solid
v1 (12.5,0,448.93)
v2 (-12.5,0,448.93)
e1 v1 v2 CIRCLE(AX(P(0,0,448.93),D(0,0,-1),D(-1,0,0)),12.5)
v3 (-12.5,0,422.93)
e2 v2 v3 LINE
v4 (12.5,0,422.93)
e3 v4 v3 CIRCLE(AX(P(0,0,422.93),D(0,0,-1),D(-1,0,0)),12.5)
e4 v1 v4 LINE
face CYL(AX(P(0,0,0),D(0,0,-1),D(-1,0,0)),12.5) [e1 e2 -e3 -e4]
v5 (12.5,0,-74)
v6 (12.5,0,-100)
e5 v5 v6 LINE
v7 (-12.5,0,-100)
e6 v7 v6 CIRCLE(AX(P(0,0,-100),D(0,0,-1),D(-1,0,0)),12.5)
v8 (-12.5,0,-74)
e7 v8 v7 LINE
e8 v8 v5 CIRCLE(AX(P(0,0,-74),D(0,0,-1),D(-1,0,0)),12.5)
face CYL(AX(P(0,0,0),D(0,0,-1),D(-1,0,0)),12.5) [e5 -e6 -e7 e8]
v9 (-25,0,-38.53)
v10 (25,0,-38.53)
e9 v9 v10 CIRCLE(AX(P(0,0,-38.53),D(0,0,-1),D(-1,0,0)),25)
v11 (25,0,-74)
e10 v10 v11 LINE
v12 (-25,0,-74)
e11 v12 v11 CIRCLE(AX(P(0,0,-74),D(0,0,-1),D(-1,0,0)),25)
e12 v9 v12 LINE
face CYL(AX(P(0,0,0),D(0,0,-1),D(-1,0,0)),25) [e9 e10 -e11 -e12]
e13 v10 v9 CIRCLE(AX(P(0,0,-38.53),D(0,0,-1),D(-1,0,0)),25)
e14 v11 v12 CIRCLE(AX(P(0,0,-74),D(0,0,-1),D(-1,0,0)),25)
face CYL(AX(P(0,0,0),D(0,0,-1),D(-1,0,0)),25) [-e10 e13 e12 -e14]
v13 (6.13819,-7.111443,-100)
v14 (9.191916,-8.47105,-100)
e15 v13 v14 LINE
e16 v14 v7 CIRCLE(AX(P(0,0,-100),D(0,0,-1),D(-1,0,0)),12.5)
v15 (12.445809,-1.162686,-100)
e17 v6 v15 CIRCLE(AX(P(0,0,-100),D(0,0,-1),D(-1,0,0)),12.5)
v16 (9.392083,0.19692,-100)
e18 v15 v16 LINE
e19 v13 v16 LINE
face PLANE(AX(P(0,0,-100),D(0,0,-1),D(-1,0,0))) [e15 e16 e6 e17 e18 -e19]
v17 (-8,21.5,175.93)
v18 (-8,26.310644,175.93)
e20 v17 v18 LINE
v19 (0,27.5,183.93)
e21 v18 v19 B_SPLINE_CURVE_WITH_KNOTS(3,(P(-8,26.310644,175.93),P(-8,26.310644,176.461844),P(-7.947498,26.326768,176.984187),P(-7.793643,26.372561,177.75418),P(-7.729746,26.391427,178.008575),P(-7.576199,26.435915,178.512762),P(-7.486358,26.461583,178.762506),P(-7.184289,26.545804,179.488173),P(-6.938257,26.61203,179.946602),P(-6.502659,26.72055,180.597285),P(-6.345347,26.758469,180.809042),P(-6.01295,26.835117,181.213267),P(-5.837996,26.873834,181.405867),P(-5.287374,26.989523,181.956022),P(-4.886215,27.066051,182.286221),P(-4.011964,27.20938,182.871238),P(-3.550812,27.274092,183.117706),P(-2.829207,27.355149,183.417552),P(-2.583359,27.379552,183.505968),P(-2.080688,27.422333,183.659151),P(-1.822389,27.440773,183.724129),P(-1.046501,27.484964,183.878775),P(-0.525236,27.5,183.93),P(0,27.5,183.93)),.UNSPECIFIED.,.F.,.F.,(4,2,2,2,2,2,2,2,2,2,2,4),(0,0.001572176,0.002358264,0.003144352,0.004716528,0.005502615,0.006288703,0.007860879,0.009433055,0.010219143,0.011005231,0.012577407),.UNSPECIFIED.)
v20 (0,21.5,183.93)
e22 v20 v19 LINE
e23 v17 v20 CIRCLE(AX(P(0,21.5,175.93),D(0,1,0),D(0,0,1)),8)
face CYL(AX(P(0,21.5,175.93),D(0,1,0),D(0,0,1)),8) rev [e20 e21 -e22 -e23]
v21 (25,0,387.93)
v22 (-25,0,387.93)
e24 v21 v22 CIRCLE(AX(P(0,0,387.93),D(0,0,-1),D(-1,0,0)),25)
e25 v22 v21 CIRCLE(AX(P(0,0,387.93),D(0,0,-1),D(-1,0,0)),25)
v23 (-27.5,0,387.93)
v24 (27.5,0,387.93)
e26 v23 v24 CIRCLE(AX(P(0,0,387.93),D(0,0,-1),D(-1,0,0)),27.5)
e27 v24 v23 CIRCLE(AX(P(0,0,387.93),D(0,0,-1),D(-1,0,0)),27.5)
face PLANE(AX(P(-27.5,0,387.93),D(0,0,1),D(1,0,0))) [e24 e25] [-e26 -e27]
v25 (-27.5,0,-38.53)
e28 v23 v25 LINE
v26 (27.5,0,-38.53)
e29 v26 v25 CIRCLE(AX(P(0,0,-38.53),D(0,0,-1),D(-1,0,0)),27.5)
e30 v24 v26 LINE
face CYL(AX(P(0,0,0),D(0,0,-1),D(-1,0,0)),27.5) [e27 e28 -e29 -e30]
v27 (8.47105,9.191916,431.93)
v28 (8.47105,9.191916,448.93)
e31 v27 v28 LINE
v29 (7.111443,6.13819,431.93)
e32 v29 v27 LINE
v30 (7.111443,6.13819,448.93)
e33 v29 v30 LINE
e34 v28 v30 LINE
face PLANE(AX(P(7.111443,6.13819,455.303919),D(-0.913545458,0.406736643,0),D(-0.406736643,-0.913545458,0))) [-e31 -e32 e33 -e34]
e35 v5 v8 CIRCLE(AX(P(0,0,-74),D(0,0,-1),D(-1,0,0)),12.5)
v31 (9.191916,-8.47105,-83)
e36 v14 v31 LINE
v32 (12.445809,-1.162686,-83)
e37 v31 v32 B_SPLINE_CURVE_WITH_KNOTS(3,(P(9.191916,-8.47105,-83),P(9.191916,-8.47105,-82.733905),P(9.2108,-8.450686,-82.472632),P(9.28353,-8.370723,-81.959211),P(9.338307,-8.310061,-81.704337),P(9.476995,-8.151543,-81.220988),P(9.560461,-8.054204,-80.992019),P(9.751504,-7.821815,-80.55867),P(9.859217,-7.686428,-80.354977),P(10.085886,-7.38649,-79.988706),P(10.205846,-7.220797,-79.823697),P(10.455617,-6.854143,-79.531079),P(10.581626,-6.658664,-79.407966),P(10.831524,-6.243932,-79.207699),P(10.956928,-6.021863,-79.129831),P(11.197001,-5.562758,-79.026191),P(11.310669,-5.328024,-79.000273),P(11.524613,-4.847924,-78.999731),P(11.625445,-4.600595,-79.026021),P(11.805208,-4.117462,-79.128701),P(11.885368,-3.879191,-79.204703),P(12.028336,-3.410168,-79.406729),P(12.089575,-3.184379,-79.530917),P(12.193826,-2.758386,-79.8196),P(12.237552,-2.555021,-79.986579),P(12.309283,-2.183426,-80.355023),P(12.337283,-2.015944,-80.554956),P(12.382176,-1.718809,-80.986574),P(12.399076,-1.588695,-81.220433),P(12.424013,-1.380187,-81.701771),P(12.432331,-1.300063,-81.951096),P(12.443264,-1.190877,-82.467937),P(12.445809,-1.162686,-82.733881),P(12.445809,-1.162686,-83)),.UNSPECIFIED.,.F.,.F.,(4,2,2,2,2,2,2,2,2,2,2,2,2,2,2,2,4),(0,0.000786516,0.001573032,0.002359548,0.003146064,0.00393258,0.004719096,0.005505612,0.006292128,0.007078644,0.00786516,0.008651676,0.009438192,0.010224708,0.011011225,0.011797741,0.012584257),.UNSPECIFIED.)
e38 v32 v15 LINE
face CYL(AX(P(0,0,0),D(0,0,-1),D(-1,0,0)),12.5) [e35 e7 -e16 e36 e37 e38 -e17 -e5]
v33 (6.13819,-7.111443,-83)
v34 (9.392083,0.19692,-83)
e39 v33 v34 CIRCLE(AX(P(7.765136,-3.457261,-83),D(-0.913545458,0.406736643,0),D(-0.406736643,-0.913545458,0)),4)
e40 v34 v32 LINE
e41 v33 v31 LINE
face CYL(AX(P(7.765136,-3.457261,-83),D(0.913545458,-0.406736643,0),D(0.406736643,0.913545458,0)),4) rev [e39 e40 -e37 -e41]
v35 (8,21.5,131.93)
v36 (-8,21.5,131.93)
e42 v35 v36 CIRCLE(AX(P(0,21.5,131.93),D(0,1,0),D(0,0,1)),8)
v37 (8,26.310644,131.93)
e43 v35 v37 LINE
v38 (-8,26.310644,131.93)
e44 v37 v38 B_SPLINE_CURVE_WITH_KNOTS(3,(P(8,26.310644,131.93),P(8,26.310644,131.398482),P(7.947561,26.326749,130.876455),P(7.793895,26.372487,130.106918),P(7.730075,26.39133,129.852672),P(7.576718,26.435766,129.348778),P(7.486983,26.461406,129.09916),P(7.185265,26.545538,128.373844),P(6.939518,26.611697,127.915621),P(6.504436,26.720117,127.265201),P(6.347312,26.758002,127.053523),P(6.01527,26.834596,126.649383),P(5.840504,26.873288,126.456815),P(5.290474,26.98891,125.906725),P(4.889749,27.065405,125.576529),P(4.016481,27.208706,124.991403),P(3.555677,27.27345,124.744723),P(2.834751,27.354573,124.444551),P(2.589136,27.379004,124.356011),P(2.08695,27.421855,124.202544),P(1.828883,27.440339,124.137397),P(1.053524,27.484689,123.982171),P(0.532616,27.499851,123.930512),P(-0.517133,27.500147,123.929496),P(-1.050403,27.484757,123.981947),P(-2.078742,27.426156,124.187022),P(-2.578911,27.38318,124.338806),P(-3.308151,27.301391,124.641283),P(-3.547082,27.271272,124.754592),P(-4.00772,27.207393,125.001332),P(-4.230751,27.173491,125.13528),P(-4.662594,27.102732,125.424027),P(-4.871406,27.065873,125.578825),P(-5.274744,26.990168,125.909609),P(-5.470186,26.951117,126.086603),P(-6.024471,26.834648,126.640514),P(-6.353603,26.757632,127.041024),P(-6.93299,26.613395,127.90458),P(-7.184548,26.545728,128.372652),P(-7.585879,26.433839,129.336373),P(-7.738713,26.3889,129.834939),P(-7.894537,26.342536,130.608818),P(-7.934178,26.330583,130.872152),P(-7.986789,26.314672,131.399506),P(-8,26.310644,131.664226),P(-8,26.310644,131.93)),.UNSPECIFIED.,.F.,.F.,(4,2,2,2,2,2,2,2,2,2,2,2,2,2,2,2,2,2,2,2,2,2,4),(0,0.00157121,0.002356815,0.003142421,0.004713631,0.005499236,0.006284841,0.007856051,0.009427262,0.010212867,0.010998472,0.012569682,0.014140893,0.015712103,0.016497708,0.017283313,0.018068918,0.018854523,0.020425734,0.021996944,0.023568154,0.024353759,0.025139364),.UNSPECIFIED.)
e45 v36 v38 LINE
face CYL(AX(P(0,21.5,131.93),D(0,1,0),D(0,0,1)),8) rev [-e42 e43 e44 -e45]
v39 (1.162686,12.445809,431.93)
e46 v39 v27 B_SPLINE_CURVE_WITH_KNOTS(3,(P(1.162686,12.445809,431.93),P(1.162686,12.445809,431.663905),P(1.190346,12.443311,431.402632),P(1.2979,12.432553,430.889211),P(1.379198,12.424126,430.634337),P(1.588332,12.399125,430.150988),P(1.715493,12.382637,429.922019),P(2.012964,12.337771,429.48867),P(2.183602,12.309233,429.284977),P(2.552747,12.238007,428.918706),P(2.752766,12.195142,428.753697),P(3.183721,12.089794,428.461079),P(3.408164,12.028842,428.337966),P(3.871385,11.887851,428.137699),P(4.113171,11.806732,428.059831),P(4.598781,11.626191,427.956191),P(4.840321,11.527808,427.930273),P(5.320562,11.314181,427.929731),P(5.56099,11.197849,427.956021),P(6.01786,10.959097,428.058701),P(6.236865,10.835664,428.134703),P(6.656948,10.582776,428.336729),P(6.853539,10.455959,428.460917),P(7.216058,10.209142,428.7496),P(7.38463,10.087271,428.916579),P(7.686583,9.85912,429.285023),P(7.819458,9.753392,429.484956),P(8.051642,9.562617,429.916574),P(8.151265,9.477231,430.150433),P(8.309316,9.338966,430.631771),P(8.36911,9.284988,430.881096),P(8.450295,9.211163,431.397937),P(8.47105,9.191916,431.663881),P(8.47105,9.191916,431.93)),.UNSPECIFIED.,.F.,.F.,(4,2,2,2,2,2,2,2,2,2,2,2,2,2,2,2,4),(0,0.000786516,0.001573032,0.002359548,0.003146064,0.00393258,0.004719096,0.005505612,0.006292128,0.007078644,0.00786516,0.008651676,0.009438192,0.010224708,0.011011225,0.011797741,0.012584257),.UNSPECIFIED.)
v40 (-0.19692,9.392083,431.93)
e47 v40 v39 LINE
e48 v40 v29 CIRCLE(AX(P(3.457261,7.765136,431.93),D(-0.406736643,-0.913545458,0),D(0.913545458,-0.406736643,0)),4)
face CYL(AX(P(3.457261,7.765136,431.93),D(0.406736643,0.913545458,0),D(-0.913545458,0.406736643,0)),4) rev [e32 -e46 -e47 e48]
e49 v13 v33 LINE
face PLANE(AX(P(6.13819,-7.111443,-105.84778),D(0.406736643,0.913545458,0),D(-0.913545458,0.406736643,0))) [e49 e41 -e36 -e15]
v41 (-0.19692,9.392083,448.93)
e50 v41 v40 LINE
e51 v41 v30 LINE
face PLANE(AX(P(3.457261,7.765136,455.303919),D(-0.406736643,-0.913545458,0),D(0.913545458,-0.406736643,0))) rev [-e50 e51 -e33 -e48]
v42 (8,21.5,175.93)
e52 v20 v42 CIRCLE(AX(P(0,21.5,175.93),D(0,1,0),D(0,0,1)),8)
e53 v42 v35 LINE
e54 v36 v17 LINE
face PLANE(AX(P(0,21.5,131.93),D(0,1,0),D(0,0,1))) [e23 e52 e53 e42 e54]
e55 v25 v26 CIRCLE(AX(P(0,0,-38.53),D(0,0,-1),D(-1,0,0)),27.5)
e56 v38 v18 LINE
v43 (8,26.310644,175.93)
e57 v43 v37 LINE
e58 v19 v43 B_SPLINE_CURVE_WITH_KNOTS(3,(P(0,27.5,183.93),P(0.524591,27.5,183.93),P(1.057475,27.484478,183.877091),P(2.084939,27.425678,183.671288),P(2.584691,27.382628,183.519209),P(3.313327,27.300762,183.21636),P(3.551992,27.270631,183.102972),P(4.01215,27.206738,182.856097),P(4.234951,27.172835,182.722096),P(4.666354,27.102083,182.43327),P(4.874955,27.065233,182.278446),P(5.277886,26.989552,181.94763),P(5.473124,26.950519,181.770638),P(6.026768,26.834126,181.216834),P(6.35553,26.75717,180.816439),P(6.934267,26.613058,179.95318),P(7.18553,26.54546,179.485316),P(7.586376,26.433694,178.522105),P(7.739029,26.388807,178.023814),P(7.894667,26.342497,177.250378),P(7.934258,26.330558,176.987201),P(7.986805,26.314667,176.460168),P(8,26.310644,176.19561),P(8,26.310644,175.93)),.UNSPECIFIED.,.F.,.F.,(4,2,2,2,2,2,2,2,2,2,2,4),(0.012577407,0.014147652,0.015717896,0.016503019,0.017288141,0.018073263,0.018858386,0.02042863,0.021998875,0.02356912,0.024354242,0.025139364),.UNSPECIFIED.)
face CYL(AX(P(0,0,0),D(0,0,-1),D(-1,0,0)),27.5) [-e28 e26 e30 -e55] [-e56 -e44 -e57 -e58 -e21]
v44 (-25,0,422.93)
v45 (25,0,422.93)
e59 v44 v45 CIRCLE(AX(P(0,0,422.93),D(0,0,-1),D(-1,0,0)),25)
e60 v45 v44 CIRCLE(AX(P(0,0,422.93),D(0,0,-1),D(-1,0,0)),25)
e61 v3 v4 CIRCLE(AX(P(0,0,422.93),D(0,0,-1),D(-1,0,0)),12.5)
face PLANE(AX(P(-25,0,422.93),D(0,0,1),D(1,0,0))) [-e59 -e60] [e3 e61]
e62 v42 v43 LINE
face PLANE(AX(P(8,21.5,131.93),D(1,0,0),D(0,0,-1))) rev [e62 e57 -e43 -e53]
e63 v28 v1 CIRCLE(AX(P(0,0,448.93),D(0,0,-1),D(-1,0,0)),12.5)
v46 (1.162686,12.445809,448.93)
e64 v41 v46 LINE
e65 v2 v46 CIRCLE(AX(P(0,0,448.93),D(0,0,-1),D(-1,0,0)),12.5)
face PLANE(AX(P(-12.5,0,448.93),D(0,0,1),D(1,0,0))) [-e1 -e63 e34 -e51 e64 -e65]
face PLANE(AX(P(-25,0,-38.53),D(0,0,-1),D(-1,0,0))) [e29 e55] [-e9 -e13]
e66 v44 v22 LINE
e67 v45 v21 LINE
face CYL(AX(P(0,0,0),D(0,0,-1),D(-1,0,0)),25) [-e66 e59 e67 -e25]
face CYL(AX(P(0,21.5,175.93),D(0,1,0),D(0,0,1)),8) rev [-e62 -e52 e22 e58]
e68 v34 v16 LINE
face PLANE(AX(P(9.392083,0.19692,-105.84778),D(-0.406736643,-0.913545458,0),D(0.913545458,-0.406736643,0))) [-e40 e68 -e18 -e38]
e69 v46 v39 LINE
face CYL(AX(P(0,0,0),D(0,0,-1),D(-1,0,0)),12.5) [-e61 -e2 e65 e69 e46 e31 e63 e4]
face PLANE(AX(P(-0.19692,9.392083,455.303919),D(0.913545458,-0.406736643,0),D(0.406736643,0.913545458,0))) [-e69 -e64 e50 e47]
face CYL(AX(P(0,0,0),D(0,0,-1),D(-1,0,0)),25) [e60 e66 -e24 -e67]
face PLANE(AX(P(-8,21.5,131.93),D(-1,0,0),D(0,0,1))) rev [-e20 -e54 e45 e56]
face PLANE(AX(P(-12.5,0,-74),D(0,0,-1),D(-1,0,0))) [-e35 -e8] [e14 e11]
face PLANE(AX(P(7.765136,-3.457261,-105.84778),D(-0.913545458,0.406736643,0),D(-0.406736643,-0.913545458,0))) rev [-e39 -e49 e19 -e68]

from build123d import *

# Parameters (mm, degrees)
CUT_EXTRUDE_3_DEPTH = 6
CUT_EXTRUDE_4_DEPTH = 7.3
CUT_EXTRUDE_5_DEPTH = 7.3


with BuildPart() as part:
    # 草图1 → 旋转1 (revolve)
    with BuildSketch(Plane(origin=(0, 0, 0), x_dir=(1, 0, 0), z_dir=(0, 1, 0))):
        Polygon((0, 100), (-12.5, 100), (-12.5, 74), (-25, 74), (-25, 38.53), (-27.5, 38.53), (-27.5, -387.93), (-25, -387.93), (-25, -422.93), (-12.5, -422.93), (-12.5, -448.93), (0, -448.93), align=None)
    revolve(axis=Axis((0, 0, 0), (0, 0, 1)))

    # 草图6 → 切除-拉伸3 (cut)
    with BuildSketch(Plane(origin=(0, 27.5, 0), x_dir=(1, 0, 0), z_dir=(0, 1, 0))):
        with BuildLine():
            Line((8, -131.93), (8, -175.93))
            ThreePointArc((8, -175.93), (0, -183.93), (-8, -175.93))
            Line((-8, -175.93), (-8, -131.93))
            ThreePointArc((-8, -131.93), (0, -123.93), (8, -131.93))
        make_face()
    extrude(amount=-CUT_EXTRUDE_3_DEPTH, mode=Mode.SUBTRACT)

    # 草图7 → 切除-拉伸4 (cut)
    with BuildSketch(Plane(origin=(14.434018231, -6.426438961, 0), x_dir=(0, 0, 1), z_dir=(-0.9135454576427331, 0.40673664307550317, 0))):
        with BuildLine():
            Line((-105.847779708, 4), (-83, 4))
            ThreePointArc((-83, 4), (-79, 0), (-83, -4))
            Line((-83, -4), (-105.847779708, -4))
            ThreePointArc((-105.847779708, -4), (-109.847779708, 0), (-105.847779708, 4))
        make_face()
    extrude(amount=CUT_EXTRUDE_4_DEPTH, mode=Mode.SUBTRACT)

    # 草图8 → 切除-拉伸5 (cut)
    with BuildSketch(Plane(origin=(6.426438961, 14.434018231, 0), x_dir=(0, 0, 1), z_dir=(-0.40673664307579893, -0.9135454576426014, 0))):
        with BuildLine():
            Line((455.303918894, -4), (431.93, -4))
            ThreePointArc((431.93, -4), (427.93, 0), (431.93, 4))
            Line((431.93, 4), (455.303918894, 4))
            ThreePointArc((455.303918894, 4), (459.303918894, 0), (455.303918894, -4))
        make_face()
    extrude(amount=CUT_EXTRUDE_5_DEPTH, mode=Mode.SUBTRACT)


solid = part.part
